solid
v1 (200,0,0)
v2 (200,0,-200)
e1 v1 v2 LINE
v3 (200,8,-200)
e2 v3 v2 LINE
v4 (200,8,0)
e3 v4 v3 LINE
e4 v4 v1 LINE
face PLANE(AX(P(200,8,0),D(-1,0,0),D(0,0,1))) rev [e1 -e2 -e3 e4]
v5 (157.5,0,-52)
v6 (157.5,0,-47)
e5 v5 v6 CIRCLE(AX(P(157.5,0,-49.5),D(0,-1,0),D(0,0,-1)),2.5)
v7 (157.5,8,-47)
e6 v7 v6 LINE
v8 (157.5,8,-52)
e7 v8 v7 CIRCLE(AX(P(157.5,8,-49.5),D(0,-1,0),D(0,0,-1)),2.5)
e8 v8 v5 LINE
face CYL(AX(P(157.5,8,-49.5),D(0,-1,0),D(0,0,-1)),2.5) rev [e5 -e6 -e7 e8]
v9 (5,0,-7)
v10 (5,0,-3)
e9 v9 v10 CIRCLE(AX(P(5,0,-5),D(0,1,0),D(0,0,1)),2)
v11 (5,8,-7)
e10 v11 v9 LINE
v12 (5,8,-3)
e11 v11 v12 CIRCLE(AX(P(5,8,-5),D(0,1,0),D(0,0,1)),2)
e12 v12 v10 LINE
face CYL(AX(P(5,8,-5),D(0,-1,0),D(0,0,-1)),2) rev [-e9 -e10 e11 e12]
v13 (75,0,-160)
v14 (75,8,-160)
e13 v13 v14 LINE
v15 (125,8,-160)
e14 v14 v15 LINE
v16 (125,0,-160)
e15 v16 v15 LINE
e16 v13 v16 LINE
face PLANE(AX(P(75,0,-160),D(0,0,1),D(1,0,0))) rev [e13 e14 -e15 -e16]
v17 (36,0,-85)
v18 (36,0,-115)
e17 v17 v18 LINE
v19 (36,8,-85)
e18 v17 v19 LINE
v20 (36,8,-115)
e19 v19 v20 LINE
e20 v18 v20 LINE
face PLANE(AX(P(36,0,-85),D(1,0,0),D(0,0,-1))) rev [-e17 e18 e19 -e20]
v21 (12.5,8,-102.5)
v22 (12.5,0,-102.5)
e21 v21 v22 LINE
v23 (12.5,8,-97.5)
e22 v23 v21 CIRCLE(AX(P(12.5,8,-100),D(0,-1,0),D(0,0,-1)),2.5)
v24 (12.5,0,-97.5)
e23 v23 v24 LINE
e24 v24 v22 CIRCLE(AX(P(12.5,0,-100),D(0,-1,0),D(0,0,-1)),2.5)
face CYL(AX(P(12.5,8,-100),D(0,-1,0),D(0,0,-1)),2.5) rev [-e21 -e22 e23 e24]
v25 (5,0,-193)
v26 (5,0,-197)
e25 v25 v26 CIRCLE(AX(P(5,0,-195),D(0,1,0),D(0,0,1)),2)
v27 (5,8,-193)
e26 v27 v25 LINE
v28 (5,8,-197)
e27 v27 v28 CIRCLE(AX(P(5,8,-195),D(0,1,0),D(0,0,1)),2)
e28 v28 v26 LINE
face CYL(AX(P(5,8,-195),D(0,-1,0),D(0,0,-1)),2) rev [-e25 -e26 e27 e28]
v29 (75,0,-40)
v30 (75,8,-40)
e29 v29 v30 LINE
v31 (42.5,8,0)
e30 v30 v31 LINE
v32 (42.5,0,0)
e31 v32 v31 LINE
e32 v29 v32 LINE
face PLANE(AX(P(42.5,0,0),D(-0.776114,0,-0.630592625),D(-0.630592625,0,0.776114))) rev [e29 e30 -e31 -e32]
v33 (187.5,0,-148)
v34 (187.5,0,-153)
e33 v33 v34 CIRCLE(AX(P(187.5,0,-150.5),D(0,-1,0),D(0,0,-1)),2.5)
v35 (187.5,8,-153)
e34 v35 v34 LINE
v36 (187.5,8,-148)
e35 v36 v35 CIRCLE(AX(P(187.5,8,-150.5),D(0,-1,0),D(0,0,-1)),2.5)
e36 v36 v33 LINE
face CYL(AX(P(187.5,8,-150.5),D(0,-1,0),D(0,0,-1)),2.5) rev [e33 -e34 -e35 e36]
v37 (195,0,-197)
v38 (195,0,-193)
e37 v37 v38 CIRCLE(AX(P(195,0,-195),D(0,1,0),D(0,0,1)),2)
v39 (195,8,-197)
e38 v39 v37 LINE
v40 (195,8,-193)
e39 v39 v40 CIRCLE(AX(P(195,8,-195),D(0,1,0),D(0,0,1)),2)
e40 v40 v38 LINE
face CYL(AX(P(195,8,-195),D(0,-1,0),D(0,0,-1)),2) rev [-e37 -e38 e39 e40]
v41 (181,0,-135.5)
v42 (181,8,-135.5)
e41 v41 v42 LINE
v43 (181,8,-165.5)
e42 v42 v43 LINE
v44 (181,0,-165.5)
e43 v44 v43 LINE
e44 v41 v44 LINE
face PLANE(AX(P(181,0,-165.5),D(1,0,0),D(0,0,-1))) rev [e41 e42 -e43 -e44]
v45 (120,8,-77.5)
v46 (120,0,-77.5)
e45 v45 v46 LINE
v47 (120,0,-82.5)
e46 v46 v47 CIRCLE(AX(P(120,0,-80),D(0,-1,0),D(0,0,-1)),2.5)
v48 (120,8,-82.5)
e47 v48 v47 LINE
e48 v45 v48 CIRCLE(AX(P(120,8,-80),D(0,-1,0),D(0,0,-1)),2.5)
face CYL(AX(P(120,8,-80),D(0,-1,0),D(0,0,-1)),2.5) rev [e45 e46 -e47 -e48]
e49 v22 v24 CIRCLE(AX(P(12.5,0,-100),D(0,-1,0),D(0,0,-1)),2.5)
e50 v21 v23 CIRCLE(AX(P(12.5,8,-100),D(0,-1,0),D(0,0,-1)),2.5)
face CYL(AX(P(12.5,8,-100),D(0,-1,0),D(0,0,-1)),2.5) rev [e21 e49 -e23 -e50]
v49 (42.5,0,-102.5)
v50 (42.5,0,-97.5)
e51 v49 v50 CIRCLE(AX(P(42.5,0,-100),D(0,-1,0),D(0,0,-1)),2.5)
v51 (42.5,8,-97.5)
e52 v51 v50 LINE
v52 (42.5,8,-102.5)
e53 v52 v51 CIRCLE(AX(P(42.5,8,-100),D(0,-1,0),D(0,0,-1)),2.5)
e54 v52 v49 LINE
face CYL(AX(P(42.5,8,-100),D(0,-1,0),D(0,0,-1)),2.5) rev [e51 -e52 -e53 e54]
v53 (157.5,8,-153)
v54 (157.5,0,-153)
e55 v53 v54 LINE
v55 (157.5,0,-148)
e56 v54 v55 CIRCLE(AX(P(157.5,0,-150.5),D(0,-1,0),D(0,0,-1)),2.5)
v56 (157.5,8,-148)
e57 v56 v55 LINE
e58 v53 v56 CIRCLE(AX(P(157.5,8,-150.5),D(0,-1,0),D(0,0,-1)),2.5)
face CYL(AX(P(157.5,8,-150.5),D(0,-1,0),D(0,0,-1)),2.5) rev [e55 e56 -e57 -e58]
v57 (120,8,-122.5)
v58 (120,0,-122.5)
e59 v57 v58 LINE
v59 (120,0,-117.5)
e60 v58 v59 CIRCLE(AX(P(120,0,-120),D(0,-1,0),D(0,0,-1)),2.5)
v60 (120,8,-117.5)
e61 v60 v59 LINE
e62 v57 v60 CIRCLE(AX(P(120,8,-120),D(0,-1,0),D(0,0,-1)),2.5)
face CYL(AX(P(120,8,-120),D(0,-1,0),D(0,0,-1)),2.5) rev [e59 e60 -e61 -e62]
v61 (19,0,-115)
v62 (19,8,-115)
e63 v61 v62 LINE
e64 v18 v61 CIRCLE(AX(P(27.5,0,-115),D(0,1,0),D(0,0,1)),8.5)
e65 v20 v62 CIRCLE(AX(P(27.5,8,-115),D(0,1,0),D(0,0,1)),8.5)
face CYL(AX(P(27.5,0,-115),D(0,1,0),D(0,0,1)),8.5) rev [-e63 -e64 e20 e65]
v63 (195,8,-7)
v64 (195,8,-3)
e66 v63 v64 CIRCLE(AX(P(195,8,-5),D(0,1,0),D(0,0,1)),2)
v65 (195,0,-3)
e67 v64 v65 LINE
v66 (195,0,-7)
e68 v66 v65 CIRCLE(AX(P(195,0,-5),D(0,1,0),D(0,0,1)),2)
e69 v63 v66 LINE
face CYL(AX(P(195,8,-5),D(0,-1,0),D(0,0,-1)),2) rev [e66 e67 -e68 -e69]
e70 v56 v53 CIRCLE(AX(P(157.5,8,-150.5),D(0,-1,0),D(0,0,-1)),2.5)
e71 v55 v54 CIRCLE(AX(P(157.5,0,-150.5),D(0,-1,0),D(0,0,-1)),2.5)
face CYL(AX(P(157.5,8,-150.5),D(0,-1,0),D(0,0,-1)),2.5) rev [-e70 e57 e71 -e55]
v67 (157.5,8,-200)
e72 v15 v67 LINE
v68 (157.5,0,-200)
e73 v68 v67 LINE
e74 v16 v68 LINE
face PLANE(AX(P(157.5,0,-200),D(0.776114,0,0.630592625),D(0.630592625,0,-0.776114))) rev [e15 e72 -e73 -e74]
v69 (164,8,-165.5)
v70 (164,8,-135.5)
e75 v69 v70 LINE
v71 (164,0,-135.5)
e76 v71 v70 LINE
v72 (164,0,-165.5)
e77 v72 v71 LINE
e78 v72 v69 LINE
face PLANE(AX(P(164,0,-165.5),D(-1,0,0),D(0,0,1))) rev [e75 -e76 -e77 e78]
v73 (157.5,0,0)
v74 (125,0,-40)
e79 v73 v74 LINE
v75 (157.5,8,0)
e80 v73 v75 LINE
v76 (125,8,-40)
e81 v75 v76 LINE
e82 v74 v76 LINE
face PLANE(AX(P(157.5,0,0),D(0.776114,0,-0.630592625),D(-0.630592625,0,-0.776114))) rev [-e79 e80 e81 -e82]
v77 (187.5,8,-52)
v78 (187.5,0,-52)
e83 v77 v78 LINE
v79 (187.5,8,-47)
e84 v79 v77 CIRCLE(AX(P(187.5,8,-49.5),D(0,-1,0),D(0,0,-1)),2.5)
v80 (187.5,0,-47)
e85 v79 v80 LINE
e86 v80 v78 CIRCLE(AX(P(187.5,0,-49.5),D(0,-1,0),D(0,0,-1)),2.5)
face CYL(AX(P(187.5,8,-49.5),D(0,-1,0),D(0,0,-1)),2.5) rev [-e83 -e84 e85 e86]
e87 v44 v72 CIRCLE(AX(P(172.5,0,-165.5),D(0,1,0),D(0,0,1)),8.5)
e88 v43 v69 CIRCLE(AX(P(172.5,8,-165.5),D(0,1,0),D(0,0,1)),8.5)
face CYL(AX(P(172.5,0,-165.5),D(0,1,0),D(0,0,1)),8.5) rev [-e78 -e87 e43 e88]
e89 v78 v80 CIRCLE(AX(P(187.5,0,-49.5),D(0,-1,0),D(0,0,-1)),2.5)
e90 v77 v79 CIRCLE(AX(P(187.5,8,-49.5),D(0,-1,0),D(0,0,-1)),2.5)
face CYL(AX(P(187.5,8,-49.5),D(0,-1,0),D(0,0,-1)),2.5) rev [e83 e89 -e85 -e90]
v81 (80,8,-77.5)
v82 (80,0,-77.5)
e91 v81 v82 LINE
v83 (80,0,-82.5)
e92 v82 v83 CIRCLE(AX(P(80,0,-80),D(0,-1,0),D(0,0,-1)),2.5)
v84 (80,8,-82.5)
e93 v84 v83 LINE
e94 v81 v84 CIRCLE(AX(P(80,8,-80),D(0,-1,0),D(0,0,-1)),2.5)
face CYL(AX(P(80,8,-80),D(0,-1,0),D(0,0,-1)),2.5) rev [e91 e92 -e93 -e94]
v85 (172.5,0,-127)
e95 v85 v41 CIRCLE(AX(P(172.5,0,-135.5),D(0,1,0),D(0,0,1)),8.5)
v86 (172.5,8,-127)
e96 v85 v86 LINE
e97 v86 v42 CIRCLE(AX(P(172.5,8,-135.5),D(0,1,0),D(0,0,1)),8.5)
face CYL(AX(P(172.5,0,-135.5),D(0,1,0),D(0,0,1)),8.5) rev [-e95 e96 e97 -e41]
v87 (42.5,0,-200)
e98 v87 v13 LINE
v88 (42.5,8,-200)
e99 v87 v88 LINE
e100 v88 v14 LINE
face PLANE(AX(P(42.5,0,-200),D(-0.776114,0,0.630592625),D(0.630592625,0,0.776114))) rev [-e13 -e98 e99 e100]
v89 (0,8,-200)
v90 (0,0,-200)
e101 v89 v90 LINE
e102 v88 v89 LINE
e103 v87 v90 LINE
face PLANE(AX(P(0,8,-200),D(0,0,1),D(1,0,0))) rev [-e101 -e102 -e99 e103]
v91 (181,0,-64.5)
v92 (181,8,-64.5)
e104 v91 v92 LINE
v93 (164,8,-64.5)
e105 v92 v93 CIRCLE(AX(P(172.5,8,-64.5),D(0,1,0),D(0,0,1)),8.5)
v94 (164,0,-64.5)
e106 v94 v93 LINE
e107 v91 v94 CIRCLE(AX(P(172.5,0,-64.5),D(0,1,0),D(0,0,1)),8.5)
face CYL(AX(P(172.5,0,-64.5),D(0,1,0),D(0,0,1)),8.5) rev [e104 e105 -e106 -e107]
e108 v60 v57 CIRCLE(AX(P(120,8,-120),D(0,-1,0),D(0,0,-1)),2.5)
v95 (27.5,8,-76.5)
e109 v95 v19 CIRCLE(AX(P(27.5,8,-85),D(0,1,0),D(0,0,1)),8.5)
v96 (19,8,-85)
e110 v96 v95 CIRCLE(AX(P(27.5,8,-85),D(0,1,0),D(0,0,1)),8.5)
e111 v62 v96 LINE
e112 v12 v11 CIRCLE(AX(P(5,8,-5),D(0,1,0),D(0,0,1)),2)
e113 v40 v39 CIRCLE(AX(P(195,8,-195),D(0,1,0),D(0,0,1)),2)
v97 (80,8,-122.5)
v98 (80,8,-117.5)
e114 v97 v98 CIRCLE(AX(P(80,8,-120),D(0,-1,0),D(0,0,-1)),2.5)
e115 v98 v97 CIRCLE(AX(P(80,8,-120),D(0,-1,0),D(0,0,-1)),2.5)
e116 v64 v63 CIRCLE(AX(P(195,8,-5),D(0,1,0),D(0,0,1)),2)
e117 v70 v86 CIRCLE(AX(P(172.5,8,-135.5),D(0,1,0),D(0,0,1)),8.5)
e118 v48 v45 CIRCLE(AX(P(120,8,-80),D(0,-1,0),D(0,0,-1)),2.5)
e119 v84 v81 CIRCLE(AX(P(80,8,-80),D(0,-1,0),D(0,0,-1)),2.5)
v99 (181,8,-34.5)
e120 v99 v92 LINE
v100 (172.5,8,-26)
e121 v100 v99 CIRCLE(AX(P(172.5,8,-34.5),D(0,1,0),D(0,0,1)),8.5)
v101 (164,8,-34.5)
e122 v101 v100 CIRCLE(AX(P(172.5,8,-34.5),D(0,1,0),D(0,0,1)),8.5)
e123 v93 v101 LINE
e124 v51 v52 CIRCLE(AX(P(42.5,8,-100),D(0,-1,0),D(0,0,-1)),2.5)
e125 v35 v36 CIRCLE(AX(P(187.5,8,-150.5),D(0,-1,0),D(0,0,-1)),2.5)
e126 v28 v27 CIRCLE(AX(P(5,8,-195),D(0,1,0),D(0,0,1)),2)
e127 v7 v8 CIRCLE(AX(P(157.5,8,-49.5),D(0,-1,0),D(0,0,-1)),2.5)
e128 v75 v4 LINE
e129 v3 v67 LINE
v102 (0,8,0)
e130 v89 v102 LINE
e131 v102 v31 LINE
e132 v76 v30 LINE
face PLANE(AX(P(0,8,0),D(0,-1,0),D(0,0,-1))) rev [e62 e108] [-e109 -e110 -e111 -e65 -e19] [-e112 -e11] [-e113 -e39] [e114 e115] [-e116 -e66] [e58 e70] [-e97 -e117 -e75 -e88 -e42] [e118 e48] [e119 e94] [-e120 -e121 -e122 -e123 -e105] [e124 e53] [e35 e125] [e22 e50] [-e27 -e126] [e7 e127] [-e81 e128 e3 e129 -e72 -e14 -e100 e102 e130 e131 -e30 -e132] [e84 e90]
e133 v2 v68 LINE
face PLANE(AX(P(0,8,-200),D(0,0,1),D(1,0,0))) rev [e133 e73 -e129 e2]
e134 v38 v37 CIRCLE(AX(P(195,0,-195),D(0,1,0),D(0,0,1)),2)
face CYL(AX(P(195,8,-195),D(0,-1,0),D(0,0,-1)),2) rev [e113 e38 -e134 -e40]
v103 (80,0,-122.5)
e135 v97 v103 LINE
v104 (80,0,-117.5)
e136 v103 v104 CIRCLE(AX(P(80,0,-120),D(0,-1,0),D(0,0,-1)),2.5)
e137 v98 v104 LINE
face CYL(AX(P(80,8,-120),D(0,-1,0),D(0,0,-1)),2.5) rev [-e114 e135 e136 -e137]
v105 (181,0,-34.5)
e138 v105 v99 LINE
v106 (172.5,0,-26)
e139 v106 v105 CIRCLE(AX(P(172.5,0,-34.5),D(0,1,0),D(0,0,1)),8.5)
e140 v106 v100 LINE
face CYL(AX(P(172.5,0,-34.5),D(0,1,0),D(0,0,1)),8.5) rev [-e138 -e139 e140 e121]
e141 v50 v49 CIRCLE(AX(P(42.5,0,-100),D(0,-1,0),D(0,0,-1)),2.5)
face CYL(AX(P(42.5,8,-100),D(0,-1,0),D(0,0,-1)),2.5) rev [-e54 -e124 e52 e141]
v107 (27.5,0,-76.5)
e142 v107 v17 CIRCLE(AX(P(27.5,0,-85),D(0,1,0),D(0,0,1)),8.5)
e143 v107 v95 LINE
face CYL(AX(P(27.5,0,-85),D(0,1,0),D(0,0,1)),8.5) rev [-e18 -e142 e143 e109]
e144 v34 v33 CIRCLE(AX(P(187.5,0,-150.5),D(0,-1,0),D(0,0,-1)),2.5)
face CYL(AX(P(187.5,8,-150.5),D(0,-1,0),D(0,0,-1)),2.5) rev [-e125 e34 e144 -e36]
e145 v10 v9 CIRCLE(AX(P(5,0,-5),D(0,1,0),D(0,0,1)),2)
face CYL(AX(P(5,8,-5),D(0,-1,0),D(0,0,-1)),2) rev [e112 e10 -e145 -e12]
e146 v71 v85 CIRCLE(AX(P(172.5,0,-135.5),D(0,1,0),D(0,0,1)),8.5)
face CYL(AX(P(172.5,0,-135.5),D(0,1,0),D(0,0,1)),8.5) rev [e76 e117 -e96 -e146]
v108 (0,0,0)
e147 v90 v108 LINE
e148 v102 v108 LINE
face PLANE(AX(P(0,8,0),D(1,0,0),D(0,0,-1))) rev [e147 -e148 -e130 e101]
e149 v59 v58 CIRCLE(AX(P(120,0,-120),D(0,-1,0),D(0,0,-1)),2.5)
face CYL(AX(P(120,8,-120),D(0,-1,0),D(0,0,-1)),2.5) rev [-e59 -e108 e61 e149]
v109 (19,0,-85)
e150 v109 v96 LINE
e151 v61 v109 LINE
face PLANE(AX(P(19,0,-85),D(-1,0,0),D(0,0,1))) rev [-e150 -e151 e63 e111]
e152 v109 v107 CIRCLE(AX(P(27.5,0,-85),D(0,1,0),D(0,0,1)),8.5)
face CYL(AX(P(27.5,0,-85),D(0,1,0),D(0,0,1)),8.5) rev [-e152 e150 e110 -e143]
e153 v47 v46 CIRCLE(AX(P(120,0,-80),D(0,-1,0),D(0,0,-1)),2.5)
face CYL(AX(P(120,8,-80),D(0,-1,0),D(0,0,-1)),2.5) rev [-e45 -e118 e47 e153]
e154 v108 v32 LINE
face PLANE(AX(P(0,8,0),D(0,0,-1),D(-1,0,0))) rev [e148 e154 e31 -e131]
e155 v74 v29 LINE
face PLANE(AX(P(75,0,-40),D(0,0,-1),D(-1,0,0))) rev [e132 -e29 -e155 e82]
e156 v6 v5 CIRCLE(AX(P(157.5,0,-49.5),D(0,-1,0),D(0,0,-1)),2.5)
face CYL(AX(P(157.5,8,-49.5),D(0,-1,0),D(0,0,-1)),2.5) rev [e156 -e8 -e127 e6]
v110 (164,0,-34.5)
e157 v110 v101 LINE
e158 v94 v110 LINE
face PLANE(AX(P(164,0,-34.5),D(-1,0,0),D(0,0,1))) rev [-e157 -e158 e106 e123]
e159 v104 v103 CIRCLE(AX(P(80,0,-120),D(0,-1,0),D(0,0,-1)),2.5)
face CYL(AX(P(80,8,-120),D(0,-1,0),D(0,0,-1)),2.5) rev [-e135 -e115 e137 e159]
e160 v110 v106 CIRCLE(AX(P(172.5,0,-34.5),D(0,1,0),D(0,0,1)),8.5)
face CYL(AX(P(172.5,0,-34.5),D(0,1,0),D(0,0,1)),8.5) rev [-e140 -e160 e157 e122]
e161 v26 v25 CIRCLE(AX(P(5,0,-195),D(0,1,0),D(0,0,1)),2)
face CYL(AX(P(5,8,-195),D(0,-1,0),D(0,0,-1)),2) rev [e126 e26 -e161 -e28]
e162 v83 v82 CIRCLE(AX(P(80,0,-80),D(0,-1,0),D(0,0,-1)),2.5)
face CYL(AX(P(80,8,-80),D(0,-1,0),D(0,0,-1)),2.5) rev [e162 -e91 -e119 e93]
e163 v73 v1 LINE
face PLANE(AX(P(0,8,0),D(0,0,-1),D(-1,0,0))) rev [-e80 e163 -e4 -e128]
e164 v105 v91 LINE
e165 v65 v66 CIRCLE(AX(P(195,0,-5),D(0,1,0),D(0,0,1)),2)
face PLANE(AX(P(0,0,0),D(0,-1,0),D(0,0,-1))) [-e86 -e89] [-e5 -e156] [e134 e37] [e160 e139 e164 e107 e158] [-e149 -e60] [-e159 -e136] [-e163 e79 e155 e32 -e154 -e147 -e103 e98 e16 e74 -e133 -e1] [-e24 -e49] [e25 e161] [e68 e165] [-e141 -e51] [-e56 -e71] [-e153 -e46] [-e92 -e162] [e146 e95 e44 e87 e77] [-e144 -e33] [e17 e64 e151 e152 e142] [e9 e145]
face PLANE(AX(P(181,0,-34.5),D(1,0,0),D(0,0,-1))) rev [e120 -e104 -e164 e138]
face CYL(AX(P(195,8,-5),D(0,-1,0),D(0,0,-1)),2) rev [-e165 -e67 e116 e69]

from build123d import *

# Parameters (mm, degrees)
SKETCH1_W           = 200
SKETCH1_H           = 200
SKETCH1_R           = 2
BOSS_EXTRUDE1_DEPTH = 8
SKETCH2_R           = 2.5
CUT_EXTRUDE1_DEPTH  = 283.955826941
CUT_EXTRUDE2_DEPTH  = 283.955826941


with BuildPart() as part:
    # Sketch1 → Boss-Extrude1 (new body)
    with BuildSketch(Plane(origin=(0, 0, 0), x_dir=(1, 0, 0), z_dir=(0, 1, 0))):
        with Locations((100, 100)):
            Rectangle(SKETCH1_W, SKETCH1_H)
        with Locations(Location((195, 195, 0), (0, 0, 270))):
            Circle(SKETCH1_R, mode=Mode.SUBTRACT)
        with Locations(Location((5, 195, 0), (0, 0, 270))):
            Circle(SKETCH1_R, mode=Mode.SUBTRACT)
        with Locations(Location((5, 5, 0), (0, 0, 270))):
            Circle(SKETCH1_R, mode=Mode.SUBTRACT)
        with Locations(Location((195, 5, 0), (0, 0, 270))):
            Circle(SKETCH1_R, mode=Mode.SUBTRACT)
    extrude(amount=BOSS_EXTRUDE1_DEPTH)

    # Sketch2 → Cut-Extrude1 (cut, through all)
    with BuildSketch(Plane.XZ):
        with Locations(Location((187.5, -49.5, 0), (0, 0, 270))):
            Circle(SKETCH2_R)
        with Locations(Location((157.5, -49.5, 0), (0, 0, 270))):
            Circle(SKETCH2_R)
        with Locations(Location((80, -120, 0), (0, 0, 270))):
            Circle(SKETCH2_R)
        with Locations(Location((80, -80, 0), (0, 0, 270))):
            Circle(SKETCH2_R)
        with Locations(Location((120, -80, 0), (0, 0, 270))):
            Circle(SKETCH2_R)
        with Locations(Location((120, -120, 0), (0, 0, 270))):
            Circle(SKETCH2_R)
        with Locations(Location((42.5, -100, 0), (0, 0, 270))):
            Circle(SKETCH2_R)
        with Locations(Location((12.5, -100, 0), (0, 0, 270))):
            Circle(SKETCH2_R)
        with Locations(Location((157.5, -150.5, 0), (0, 0, 270))):
            Circle(SKETCH2_R)
        with Locations(Location((187.5, -150.5, 0), (0, 0, 270))):
            Circle(SKETCH2_R)
    extrude(amount=-CUT_EXTRUDE1_DEPTH, mode=Mode.SUBTRACT)

    # Sketch3 → Cut-Extrude2 (cut, through all)
    with BuildSketch(Plane(origin=(0, 8, 0), x_dir=(1, 0, 0), z_dir=(0, 1, 0))):
        Polygon((42.5, 200), (75, 160), (125, 160), (157.5, 200), align=None)
        Polygon((42.5, 0), (157.5, 0), (125, 40), (75, 40), align=None)
        with BuildLine():
            Line((19, 85), (19, 115))
            ThreePointArc((19, 115), (27.5, 123.5), (36, 115))
            Line((36, 115), (36, 85))
            ThreePointArc((36, 85), (27.5, 76.5), (19, 85))
        make_face()
        with BuildLine():
            Line((181, 34.5), (181, 64.5))
            ThreePointArc((181, 64.5), (172.5, 73), (164, 64.5))
            Line((164, 64.5), (164, 34.5))
            ThreePointArc((164, 34.5), (172.5, 26), (181, 34.5))
        make_face()
        with BuildLine():
            Line((181, 165.5), (181, 135.5))
            ThreePointArc((181, 135.5), (172.5, 127), (164, 135.5))
            Line((164, 135.5), (164, 165.5))
            ThreePointArc((164, 165.5), (172.5, 174), (181, 165.5))
        make_face()
    extrude(amount=-CUT_EXTRUDE2_DEPTH, mode=Mode.SUBTRACT)


solid = part.part
